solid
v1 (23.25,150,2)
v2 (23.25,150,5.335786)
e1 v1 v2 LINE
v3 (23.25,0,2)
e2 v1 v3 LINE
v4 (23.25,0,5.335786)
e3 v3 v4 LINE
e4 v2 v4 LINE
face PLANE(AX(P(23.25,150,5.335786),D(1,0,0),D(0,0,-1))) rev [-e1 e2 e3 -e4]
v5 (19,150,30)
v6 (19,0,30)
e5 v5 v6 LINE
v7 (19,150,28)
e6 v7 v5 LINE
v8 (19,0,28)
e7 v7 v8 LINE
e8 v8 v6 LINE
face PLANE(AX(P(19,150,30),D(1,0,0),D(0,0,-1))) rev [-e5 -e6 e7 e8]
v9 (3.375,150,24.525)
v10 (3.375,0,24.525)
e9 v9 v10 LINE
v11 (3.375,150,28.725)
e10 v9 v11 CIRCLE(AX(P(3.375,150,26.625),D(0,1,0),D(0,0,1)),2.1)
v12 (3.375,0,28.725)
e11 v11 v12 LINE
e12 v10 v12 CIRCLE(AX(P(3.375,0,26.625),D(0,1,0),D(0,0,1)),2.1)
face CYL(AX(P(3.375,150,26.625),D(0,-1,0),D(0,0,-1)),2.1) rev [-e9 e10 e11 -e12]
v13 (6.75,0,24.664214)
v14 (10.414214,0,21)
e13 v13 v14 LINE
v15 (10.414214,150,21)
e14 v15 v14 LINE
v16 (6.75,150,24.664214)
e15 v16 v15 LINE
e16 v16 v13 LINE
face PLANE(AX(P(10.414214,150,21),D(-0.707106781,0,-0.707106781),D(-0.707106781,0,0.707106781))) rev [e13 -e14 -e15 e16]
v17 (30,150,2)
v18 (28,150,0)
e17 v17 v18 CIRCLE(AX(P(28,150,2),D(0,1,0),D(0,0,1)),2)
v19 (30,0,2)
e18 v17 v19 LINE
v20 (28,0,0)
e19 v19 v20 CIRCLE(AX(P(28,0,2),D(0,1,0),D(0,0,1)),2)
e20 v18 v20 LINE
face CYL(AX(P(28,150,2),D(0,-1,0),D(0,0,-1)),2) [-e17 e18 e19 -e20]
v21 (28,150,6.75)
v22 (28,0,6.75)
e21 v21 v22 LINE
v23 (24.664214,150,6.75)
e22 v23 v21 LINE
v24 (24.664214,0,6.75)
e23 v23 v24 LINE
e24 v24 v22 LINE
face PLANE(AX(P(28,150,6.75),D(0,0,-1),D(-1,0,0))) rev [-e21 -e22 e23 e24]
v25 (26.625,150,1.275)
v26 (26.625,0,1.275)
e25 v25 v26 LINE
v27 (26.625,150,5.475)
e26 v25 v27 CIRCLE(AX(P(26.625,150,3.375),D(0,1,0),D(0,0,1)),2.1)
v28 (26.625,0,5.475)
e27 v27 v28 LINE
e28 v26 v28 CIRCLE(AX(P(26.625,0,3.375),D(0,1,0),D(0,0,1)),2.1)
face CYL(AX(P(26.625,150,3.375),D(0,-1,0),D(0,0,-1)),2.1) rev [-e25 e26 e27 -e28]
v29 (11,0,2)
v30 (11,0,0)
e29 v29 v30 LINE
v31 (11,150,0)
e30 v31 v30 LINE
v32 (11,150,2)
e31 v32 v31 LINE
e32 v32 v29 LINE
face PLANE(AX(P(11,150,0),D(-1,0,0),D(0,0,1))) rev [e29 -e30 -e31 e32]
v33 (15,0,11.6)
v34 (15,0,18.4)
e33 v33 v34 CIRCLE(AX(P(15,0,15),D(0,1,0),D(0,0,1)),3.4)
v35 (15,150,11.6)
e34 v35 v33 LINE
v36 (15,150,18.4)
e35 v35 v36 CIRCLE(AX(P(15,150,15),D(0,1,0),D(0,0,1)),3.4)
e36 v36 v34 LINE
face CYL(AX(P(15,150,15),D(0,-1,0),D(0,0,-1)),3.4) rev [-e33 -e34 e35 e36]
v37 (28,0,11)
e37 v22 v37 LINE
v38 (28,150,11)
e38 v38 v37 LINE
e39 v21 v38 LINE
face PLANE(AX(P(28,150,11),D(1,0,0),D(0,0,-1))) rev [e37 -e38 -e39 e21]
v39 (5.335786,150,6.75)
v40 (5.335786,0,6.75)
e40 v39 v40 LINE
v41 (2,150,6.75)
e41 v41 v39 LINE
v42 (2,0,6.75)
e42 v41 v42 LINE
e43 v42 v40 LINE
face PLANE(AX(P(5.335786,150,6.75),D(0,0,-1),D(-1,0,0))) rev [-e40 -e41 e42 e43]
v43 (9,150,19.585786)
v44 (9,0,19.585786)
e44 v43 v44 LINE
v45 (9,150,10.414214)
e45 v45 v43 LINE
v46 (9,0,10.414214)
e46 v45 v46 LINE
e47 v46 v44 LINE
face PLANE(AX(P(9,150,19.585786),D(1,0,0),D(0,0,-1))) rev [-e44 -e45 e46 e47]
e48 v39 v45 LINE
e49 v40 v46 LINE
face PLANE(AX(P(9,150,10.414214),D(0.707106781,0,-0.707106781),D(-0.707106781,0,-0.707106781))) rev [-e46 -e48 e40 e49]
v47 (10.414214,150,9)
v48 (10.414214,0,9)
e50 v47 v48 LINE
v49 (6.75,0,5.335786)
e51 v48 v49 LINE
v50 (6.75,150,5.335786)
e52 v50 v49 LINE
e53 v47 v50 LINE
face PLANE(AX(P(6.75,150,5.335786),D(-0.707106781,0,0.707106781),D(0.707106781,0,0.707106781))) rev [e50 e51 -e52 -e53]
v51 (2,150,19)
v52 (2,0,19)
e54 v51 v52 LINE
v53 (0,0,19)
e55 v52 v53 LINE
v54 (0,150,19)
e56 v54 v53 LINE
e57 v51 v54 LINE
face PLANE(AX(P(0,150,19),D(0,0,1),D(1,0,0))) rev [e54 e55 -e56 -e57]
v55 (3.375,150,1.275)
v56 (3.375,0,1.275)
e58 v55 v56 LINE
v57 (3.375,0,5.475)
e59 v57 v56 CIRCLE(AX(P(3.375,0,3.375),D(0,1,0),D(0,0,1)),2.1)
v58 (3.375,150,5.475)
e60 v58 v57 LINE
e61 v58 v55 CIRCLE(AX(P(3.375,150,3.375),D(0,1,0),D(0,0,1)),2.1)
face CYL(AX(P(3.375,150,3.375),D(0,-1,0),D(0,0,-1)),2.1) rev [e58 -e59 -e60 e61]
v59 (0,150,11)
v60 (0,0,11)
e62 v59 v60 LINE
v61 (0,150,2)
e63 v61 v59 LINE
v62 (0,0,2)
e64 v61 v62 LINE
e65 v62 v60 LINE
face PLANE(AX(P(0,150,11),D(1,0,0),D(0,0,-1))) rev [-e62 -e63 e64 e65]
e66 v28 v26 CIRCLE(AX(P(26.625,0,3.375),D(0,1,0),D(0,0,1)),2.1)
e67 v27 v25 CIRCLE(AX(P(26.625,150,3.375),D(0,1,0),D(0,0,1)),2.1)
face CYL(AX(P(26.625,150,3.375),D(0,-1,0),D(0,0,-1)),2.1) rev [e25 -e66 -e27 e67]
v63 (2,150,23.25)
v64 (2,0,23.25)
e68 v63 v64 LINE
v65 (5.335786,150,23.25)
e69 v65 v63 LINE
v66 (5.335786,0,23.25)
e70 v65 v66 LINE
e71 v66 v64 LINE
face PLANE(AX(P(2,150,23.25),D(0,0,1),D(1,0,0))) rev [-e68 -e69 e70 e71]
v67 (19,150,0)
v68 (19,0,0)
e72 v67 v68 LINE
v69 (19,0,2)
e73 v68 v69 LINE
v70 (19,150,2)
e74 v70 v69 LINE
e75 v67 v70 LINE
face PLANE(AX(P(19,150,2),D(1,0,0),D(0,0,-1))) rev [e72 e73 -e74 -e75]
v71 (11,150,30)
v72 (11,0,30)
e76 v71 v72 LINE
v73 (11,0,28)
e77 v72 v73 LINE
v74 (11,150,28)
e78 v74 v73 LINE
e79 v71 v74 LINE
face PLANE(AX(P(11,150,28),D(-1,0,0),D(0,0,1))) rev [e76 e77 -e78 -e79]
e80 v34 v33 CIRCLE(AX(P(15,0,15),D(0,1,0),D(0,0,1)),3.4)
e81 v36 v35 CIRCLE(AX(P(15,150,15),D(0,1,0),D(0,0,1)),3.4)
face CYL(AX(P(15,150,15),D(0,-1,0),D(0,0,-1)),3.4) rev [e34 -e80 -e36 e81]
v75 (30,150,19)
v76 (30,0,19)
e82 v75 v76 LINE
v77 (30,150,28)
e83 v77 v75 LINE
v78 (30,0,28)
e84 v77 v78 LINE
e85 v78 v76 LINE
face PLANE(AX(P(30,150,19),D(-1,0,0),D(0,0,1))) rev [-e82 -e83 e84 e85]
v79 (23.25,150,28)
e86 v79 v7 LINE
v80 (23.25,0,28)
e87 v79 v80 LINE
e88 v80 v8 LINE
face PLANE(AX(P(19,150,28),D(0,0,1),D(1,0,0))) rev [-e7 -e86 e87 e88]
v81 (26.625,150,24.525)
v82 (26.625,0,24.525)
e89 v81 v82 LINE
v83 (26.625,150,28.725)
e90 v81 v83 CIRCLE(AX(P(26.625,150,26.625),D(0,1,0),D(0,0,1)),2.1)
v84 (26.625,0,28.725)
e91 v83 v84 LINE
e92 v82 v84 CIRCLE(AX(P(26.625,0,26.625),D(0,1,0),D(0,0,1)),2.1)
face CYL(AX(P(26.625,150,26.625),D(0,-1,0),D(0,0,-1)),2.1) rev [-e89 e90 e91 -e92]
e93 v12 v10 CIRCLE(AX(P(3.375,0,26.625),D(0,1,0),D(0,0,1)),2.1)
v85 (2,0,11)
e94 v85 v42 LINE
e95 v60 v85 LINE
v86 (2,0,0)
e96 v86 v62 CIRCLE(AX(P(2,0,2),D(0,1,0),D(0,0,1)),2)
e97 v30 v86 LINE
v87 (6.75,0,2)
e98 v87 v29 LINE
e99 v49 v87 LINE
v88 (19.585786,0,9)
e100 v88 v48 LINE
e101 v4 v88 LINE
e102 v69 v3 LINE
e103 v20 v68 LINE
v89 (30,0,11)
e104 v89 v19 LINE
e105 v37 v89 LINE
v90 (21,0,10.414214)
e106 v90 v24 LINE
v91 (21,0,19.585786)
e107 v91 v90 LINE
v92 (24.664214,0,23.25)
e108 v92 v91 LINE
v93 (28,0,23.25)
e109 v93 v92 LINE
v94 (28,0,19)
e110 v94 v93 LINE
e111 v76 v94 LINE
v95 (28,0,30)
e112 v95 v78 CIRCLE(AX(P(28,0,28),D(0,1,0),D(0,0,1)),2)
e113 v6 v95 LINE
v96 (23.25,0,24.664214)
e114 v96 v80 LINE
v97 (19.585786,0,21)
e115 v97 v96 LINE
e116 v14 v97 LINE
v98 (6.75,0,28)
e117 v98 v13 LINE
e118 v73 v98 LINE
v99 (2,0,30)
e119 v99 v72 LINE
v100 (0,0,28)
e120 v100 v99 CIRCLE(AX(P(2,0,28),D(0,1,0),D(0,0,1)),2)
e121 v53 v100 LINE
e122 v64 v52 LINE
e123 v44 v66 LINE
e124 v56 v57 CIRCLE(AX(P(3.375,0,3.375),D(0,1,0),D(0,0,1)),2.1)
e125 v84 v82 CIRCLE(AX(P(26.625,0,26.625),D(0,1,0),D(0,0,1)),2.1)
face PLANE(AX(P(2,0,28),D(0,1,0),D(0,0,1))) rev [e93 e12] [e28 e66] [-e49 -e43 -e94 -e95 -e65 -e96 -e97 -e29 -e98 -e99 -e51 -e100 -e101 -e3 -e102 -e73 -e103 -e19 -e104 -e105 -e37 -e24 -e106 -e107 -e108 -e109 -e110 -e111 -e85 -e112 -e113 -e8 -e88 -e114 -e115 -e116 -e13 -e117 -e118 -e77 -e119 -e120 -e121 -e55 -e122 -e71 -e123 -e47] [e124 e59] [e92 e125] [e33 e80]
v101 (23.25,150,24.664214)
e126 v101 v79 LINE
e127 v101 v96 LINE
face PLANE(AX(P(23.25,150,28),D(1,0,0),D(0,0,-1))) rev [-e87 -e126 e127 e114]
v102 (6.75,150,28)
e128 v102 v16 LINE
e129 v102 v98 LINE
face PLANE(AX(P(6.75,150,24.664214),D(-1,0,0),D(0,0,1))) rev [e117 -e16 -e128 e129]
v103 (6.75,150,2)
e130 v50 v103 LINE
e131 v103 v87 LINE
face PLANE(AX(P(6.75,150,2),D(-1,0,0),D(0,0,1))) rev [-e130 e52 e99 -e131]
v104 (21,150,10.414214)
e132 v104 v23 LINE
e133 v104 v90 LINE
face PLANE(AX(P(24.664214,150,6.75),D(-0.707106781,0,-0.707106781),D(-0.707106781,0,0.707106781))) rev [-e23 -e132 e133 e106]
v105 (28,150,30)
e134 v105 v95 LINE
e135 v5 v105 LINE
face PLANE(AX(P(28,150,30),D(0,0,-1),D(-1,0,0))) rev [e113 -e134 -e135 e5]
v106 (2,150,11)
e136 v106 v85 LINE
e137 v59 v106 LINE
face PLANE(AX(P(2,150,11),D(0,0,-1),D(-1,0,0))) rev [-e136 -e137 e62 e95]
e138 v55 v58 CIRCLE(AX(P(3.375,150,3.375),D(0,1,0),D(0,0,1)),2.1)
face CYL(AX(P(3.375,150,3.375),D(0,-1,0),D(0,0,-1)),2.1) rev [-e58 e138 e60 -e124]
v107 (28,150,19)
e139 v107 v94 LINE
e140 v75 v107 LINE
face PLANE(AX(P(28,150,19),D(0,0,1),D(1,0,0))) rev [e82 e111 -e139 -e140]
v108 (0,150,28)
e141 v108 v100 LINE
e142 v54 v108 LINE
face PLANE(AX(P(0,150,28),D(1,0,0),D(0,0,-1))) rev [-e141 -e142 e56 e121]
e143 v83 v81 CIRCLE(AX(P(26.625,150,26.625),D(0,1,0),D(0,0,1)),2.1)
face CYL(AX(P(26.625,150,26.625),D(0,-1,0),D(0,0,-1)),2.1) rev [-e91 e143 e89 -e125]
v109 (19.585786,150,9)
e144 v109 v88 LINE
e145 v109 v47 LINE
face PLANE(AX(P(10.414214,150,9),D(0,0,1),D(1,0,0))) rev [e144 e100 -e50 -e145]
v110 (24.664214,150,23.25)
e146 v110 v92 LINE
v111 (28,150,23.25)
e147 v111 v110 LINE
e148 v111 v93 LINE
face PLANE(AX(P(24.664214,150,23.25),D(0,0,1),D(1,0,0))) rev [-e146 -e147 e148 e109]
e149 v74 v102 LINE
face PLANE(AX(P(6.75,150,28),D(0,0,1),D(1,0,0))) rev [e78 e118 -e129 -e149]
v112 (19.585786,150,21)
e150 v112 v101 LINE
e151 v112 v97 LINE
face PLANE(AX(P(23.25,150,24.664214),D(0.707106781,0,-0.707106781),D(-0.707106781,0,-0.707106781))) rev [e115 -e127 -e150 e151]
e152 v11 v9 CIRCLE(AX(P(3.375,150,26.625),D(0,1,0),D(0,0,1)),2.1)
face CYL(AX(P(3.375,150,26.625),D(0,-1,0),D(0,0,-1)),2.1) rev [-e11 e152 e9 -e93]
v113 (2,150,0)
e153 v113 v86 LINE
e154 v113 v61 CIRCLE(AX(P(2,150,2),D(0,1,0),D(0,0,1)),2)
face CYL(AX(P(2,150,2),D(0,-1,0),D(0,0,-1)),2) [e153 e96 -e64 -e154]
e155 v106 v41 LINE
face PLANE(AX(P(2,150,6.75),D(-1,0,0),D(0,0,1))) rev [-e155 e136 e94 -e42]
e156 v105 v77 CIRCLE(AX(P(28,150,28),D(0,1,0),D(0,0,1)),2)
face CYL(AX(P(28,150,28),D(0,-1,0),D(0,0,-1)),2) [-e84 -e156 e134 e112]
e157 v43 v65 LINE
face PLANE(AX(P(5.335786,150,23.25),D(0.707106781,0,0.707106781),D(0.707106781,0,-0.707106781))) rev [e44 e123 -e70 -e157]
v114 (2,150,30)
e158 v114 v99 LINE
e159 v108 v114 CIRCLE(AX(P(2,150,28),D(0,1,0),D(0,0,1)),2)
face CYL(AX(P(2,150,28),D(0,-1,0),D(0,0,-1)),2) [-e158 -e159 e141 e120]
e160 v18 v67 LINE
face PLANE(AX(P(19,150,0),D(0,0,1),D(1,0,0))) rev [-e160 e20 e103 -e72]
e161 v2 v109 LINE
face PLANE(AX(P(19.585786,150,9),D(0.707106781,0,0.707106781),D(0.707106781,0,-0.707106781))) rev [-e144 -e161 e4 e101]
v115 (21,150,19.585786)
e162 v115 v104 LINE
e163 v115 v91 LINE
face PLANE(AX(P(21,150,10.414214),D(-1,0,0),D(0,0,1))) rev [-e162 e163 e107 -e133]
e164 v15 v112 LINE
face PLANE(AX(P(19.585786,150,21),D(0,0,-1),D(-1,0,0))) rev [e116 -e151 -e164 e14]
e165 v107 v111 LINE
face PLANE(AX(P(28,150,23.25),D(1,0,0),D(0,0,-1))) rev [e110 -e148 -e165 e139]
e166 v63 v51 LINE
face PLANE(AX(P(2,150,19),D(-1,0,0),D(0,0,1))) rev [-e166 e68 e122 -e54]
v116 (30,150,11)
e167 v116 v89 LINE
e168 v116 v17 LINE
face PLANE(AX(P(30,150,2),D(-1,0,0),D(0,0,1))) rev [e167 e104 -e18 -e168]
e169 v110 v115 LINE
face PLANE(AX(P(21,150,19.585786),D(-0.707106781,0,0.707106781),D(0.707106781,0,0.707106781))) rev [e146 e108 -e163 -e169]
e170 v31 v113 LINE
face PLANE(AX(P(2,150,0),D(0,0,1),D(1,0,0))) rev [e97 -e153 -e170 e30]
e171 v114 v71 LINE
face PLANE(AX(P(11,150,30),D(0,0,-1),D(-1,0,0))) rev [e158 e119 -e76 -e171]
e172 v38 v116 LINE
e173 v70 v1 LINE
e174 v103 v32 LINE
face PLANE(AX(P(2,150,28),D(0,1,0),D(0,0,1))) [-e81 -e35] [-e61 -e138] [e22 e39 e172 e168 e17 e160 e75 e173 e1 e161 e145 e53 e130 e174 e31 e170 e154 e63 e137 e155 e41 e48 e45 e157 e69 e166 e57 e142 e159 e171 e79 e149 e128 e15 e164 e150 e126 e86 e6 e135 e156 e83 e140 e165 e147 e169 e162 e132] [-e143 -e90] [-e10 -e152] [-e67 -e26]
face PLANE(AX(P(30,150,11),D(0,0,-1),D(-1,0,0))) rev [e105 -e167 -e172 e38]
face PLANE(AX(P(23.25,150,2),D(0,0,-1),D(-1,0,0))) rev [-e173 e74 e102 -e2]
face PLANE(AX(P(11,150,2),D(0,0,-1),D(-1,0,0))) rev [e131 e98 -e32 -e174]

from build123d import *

# Parameters (mm, degrees)
SKETCH_1_R      = 2.1
SKETCH_1_R_2    = 3.4
EXTRUDE_1_DEPTH = 150


with BuildPart() as part:
    # 草图1 → 拉伸1 (new body)
    with BuildSketch(Plane(origin=(0, 0, 0), x_dir=(1, 0, 0), z_dir=(0, 1, 0))):
        with BuildLine():
            Line((6.75, -28), (11, -28))
            Line((11, -28), (11, -30))
            Line((11, -30), (2, -30))
            ThreePointArc((2, -30), (0.585786438, -29.414213562), (0, -28))
            Line((0, -28), (0, -19))
            Line((0, -19), (2, -19))
            Line((2, -19), (2, -23.25))
            Line((2, -23.25), (5.335785999, -23.25))
            Line((5.335785999, -23.25), (9, -19.585785999))
            Line((9, -19.585785999), (9, -10.414214001))
            Line((9, -10.414214001), (5.335785999, -6.75))
            Line((5.335785999, -6.75), (2, -6.75))
            Line((2, -6.75), (2, -11))
            Line((2, -11), (0, -11))
            Line((0, -11), (0, -2))
            ThreePointArc((0, -2), (0.585786438, -0.585786438), (2, 0))
            Line((2, 0), (11, 0))
            Line((11, 0), (11, -2))
            Line((11, -2), (6.75, -2))
            Line((6.75, -2), (6.75, -5.335785999))
            Line((6.75, -5.335785999), (10.414214001, -9))
            Line((10.414214001, -9), (19.585785999, -9))
            Line((19.585785999, -9), (23.25, -5.335785999))
            Line((23.25, -5.335785999), (23.25, -2))
            Line((23.25, -2), (19, -2))
            Line((19, -2), (19, 0))
            Line((19, 0), (28, 0))
            ThreePointArc((28, 0), (29.414213562, -0.585786438), (30, -2))
            Line((30, -2), (30, -11))
            Line((30, -11), (28, -11))
            Line((28, -11), (28, -6.75))
            Line((28, -6.75), (24.664214001, -6.75))
            Line((24.664214001, -6.75), (21, -10.414214001))
            Line((21, -10.414214001), (21, -19.585785999))
            Line((21, -19.585785999), (24.664214001, -23.25))
            Line((24.664214001, -23.25), (28, -23.25))
            Line((28, -23.25), (28, -19))
            Line((28, -19), (30, -19))
            Line((30, -19), (30, -28))
            ThreePointArc((30, -28), (29.414213562, -29.414213562), (28, -30))
            Line((28, -30), (19, -30))
            Line((19, -30), (19, -28))
            Line((19, -28), (23.25, -28))
            Line((23.25, -28), (23.25, -24.664214001))
            Line((23.25, -24.664214001), (19.585785999, -21))
            Line((19.585785999, -21), (10.414214001, -21))
            Line((10.414214001, -21), (6.75, -24.664214001))
            Line((6.75, -24.664214001), (6.75, -28))
        make_face()
        with Locations(Location((3.375, -26.625, 0), (0, 0, 270))):
            Circle(SKETCH_1_R, mode=Mode.SUBTRACT)
        with Locations(Location((26.625, -26.625, 0), (0, 0, 270))):
            Circle(SKETCH_1_R, mode=Mode.SUBTRACT)
        with Locations(Location((15, -15, 0), (0, 0, 270))):
            Circle(SKETCH_1_R_2, mode=Mode.SUBTRACT)
        with Locations(Location((3.375, -3.375, 0), (0, 0, 270))):
            Circle(SKETCH_1_R, mode=Mode.SUBTRACT)
        with Locations(Location((26.625, -3.375, 0), (0, 0, 270))):
            Circle(SKETCH_1_R, mode=Mode.SUBTRACT)
    extrude(amount=EXTRUDE_1_DEPTH)


solid = part.part
